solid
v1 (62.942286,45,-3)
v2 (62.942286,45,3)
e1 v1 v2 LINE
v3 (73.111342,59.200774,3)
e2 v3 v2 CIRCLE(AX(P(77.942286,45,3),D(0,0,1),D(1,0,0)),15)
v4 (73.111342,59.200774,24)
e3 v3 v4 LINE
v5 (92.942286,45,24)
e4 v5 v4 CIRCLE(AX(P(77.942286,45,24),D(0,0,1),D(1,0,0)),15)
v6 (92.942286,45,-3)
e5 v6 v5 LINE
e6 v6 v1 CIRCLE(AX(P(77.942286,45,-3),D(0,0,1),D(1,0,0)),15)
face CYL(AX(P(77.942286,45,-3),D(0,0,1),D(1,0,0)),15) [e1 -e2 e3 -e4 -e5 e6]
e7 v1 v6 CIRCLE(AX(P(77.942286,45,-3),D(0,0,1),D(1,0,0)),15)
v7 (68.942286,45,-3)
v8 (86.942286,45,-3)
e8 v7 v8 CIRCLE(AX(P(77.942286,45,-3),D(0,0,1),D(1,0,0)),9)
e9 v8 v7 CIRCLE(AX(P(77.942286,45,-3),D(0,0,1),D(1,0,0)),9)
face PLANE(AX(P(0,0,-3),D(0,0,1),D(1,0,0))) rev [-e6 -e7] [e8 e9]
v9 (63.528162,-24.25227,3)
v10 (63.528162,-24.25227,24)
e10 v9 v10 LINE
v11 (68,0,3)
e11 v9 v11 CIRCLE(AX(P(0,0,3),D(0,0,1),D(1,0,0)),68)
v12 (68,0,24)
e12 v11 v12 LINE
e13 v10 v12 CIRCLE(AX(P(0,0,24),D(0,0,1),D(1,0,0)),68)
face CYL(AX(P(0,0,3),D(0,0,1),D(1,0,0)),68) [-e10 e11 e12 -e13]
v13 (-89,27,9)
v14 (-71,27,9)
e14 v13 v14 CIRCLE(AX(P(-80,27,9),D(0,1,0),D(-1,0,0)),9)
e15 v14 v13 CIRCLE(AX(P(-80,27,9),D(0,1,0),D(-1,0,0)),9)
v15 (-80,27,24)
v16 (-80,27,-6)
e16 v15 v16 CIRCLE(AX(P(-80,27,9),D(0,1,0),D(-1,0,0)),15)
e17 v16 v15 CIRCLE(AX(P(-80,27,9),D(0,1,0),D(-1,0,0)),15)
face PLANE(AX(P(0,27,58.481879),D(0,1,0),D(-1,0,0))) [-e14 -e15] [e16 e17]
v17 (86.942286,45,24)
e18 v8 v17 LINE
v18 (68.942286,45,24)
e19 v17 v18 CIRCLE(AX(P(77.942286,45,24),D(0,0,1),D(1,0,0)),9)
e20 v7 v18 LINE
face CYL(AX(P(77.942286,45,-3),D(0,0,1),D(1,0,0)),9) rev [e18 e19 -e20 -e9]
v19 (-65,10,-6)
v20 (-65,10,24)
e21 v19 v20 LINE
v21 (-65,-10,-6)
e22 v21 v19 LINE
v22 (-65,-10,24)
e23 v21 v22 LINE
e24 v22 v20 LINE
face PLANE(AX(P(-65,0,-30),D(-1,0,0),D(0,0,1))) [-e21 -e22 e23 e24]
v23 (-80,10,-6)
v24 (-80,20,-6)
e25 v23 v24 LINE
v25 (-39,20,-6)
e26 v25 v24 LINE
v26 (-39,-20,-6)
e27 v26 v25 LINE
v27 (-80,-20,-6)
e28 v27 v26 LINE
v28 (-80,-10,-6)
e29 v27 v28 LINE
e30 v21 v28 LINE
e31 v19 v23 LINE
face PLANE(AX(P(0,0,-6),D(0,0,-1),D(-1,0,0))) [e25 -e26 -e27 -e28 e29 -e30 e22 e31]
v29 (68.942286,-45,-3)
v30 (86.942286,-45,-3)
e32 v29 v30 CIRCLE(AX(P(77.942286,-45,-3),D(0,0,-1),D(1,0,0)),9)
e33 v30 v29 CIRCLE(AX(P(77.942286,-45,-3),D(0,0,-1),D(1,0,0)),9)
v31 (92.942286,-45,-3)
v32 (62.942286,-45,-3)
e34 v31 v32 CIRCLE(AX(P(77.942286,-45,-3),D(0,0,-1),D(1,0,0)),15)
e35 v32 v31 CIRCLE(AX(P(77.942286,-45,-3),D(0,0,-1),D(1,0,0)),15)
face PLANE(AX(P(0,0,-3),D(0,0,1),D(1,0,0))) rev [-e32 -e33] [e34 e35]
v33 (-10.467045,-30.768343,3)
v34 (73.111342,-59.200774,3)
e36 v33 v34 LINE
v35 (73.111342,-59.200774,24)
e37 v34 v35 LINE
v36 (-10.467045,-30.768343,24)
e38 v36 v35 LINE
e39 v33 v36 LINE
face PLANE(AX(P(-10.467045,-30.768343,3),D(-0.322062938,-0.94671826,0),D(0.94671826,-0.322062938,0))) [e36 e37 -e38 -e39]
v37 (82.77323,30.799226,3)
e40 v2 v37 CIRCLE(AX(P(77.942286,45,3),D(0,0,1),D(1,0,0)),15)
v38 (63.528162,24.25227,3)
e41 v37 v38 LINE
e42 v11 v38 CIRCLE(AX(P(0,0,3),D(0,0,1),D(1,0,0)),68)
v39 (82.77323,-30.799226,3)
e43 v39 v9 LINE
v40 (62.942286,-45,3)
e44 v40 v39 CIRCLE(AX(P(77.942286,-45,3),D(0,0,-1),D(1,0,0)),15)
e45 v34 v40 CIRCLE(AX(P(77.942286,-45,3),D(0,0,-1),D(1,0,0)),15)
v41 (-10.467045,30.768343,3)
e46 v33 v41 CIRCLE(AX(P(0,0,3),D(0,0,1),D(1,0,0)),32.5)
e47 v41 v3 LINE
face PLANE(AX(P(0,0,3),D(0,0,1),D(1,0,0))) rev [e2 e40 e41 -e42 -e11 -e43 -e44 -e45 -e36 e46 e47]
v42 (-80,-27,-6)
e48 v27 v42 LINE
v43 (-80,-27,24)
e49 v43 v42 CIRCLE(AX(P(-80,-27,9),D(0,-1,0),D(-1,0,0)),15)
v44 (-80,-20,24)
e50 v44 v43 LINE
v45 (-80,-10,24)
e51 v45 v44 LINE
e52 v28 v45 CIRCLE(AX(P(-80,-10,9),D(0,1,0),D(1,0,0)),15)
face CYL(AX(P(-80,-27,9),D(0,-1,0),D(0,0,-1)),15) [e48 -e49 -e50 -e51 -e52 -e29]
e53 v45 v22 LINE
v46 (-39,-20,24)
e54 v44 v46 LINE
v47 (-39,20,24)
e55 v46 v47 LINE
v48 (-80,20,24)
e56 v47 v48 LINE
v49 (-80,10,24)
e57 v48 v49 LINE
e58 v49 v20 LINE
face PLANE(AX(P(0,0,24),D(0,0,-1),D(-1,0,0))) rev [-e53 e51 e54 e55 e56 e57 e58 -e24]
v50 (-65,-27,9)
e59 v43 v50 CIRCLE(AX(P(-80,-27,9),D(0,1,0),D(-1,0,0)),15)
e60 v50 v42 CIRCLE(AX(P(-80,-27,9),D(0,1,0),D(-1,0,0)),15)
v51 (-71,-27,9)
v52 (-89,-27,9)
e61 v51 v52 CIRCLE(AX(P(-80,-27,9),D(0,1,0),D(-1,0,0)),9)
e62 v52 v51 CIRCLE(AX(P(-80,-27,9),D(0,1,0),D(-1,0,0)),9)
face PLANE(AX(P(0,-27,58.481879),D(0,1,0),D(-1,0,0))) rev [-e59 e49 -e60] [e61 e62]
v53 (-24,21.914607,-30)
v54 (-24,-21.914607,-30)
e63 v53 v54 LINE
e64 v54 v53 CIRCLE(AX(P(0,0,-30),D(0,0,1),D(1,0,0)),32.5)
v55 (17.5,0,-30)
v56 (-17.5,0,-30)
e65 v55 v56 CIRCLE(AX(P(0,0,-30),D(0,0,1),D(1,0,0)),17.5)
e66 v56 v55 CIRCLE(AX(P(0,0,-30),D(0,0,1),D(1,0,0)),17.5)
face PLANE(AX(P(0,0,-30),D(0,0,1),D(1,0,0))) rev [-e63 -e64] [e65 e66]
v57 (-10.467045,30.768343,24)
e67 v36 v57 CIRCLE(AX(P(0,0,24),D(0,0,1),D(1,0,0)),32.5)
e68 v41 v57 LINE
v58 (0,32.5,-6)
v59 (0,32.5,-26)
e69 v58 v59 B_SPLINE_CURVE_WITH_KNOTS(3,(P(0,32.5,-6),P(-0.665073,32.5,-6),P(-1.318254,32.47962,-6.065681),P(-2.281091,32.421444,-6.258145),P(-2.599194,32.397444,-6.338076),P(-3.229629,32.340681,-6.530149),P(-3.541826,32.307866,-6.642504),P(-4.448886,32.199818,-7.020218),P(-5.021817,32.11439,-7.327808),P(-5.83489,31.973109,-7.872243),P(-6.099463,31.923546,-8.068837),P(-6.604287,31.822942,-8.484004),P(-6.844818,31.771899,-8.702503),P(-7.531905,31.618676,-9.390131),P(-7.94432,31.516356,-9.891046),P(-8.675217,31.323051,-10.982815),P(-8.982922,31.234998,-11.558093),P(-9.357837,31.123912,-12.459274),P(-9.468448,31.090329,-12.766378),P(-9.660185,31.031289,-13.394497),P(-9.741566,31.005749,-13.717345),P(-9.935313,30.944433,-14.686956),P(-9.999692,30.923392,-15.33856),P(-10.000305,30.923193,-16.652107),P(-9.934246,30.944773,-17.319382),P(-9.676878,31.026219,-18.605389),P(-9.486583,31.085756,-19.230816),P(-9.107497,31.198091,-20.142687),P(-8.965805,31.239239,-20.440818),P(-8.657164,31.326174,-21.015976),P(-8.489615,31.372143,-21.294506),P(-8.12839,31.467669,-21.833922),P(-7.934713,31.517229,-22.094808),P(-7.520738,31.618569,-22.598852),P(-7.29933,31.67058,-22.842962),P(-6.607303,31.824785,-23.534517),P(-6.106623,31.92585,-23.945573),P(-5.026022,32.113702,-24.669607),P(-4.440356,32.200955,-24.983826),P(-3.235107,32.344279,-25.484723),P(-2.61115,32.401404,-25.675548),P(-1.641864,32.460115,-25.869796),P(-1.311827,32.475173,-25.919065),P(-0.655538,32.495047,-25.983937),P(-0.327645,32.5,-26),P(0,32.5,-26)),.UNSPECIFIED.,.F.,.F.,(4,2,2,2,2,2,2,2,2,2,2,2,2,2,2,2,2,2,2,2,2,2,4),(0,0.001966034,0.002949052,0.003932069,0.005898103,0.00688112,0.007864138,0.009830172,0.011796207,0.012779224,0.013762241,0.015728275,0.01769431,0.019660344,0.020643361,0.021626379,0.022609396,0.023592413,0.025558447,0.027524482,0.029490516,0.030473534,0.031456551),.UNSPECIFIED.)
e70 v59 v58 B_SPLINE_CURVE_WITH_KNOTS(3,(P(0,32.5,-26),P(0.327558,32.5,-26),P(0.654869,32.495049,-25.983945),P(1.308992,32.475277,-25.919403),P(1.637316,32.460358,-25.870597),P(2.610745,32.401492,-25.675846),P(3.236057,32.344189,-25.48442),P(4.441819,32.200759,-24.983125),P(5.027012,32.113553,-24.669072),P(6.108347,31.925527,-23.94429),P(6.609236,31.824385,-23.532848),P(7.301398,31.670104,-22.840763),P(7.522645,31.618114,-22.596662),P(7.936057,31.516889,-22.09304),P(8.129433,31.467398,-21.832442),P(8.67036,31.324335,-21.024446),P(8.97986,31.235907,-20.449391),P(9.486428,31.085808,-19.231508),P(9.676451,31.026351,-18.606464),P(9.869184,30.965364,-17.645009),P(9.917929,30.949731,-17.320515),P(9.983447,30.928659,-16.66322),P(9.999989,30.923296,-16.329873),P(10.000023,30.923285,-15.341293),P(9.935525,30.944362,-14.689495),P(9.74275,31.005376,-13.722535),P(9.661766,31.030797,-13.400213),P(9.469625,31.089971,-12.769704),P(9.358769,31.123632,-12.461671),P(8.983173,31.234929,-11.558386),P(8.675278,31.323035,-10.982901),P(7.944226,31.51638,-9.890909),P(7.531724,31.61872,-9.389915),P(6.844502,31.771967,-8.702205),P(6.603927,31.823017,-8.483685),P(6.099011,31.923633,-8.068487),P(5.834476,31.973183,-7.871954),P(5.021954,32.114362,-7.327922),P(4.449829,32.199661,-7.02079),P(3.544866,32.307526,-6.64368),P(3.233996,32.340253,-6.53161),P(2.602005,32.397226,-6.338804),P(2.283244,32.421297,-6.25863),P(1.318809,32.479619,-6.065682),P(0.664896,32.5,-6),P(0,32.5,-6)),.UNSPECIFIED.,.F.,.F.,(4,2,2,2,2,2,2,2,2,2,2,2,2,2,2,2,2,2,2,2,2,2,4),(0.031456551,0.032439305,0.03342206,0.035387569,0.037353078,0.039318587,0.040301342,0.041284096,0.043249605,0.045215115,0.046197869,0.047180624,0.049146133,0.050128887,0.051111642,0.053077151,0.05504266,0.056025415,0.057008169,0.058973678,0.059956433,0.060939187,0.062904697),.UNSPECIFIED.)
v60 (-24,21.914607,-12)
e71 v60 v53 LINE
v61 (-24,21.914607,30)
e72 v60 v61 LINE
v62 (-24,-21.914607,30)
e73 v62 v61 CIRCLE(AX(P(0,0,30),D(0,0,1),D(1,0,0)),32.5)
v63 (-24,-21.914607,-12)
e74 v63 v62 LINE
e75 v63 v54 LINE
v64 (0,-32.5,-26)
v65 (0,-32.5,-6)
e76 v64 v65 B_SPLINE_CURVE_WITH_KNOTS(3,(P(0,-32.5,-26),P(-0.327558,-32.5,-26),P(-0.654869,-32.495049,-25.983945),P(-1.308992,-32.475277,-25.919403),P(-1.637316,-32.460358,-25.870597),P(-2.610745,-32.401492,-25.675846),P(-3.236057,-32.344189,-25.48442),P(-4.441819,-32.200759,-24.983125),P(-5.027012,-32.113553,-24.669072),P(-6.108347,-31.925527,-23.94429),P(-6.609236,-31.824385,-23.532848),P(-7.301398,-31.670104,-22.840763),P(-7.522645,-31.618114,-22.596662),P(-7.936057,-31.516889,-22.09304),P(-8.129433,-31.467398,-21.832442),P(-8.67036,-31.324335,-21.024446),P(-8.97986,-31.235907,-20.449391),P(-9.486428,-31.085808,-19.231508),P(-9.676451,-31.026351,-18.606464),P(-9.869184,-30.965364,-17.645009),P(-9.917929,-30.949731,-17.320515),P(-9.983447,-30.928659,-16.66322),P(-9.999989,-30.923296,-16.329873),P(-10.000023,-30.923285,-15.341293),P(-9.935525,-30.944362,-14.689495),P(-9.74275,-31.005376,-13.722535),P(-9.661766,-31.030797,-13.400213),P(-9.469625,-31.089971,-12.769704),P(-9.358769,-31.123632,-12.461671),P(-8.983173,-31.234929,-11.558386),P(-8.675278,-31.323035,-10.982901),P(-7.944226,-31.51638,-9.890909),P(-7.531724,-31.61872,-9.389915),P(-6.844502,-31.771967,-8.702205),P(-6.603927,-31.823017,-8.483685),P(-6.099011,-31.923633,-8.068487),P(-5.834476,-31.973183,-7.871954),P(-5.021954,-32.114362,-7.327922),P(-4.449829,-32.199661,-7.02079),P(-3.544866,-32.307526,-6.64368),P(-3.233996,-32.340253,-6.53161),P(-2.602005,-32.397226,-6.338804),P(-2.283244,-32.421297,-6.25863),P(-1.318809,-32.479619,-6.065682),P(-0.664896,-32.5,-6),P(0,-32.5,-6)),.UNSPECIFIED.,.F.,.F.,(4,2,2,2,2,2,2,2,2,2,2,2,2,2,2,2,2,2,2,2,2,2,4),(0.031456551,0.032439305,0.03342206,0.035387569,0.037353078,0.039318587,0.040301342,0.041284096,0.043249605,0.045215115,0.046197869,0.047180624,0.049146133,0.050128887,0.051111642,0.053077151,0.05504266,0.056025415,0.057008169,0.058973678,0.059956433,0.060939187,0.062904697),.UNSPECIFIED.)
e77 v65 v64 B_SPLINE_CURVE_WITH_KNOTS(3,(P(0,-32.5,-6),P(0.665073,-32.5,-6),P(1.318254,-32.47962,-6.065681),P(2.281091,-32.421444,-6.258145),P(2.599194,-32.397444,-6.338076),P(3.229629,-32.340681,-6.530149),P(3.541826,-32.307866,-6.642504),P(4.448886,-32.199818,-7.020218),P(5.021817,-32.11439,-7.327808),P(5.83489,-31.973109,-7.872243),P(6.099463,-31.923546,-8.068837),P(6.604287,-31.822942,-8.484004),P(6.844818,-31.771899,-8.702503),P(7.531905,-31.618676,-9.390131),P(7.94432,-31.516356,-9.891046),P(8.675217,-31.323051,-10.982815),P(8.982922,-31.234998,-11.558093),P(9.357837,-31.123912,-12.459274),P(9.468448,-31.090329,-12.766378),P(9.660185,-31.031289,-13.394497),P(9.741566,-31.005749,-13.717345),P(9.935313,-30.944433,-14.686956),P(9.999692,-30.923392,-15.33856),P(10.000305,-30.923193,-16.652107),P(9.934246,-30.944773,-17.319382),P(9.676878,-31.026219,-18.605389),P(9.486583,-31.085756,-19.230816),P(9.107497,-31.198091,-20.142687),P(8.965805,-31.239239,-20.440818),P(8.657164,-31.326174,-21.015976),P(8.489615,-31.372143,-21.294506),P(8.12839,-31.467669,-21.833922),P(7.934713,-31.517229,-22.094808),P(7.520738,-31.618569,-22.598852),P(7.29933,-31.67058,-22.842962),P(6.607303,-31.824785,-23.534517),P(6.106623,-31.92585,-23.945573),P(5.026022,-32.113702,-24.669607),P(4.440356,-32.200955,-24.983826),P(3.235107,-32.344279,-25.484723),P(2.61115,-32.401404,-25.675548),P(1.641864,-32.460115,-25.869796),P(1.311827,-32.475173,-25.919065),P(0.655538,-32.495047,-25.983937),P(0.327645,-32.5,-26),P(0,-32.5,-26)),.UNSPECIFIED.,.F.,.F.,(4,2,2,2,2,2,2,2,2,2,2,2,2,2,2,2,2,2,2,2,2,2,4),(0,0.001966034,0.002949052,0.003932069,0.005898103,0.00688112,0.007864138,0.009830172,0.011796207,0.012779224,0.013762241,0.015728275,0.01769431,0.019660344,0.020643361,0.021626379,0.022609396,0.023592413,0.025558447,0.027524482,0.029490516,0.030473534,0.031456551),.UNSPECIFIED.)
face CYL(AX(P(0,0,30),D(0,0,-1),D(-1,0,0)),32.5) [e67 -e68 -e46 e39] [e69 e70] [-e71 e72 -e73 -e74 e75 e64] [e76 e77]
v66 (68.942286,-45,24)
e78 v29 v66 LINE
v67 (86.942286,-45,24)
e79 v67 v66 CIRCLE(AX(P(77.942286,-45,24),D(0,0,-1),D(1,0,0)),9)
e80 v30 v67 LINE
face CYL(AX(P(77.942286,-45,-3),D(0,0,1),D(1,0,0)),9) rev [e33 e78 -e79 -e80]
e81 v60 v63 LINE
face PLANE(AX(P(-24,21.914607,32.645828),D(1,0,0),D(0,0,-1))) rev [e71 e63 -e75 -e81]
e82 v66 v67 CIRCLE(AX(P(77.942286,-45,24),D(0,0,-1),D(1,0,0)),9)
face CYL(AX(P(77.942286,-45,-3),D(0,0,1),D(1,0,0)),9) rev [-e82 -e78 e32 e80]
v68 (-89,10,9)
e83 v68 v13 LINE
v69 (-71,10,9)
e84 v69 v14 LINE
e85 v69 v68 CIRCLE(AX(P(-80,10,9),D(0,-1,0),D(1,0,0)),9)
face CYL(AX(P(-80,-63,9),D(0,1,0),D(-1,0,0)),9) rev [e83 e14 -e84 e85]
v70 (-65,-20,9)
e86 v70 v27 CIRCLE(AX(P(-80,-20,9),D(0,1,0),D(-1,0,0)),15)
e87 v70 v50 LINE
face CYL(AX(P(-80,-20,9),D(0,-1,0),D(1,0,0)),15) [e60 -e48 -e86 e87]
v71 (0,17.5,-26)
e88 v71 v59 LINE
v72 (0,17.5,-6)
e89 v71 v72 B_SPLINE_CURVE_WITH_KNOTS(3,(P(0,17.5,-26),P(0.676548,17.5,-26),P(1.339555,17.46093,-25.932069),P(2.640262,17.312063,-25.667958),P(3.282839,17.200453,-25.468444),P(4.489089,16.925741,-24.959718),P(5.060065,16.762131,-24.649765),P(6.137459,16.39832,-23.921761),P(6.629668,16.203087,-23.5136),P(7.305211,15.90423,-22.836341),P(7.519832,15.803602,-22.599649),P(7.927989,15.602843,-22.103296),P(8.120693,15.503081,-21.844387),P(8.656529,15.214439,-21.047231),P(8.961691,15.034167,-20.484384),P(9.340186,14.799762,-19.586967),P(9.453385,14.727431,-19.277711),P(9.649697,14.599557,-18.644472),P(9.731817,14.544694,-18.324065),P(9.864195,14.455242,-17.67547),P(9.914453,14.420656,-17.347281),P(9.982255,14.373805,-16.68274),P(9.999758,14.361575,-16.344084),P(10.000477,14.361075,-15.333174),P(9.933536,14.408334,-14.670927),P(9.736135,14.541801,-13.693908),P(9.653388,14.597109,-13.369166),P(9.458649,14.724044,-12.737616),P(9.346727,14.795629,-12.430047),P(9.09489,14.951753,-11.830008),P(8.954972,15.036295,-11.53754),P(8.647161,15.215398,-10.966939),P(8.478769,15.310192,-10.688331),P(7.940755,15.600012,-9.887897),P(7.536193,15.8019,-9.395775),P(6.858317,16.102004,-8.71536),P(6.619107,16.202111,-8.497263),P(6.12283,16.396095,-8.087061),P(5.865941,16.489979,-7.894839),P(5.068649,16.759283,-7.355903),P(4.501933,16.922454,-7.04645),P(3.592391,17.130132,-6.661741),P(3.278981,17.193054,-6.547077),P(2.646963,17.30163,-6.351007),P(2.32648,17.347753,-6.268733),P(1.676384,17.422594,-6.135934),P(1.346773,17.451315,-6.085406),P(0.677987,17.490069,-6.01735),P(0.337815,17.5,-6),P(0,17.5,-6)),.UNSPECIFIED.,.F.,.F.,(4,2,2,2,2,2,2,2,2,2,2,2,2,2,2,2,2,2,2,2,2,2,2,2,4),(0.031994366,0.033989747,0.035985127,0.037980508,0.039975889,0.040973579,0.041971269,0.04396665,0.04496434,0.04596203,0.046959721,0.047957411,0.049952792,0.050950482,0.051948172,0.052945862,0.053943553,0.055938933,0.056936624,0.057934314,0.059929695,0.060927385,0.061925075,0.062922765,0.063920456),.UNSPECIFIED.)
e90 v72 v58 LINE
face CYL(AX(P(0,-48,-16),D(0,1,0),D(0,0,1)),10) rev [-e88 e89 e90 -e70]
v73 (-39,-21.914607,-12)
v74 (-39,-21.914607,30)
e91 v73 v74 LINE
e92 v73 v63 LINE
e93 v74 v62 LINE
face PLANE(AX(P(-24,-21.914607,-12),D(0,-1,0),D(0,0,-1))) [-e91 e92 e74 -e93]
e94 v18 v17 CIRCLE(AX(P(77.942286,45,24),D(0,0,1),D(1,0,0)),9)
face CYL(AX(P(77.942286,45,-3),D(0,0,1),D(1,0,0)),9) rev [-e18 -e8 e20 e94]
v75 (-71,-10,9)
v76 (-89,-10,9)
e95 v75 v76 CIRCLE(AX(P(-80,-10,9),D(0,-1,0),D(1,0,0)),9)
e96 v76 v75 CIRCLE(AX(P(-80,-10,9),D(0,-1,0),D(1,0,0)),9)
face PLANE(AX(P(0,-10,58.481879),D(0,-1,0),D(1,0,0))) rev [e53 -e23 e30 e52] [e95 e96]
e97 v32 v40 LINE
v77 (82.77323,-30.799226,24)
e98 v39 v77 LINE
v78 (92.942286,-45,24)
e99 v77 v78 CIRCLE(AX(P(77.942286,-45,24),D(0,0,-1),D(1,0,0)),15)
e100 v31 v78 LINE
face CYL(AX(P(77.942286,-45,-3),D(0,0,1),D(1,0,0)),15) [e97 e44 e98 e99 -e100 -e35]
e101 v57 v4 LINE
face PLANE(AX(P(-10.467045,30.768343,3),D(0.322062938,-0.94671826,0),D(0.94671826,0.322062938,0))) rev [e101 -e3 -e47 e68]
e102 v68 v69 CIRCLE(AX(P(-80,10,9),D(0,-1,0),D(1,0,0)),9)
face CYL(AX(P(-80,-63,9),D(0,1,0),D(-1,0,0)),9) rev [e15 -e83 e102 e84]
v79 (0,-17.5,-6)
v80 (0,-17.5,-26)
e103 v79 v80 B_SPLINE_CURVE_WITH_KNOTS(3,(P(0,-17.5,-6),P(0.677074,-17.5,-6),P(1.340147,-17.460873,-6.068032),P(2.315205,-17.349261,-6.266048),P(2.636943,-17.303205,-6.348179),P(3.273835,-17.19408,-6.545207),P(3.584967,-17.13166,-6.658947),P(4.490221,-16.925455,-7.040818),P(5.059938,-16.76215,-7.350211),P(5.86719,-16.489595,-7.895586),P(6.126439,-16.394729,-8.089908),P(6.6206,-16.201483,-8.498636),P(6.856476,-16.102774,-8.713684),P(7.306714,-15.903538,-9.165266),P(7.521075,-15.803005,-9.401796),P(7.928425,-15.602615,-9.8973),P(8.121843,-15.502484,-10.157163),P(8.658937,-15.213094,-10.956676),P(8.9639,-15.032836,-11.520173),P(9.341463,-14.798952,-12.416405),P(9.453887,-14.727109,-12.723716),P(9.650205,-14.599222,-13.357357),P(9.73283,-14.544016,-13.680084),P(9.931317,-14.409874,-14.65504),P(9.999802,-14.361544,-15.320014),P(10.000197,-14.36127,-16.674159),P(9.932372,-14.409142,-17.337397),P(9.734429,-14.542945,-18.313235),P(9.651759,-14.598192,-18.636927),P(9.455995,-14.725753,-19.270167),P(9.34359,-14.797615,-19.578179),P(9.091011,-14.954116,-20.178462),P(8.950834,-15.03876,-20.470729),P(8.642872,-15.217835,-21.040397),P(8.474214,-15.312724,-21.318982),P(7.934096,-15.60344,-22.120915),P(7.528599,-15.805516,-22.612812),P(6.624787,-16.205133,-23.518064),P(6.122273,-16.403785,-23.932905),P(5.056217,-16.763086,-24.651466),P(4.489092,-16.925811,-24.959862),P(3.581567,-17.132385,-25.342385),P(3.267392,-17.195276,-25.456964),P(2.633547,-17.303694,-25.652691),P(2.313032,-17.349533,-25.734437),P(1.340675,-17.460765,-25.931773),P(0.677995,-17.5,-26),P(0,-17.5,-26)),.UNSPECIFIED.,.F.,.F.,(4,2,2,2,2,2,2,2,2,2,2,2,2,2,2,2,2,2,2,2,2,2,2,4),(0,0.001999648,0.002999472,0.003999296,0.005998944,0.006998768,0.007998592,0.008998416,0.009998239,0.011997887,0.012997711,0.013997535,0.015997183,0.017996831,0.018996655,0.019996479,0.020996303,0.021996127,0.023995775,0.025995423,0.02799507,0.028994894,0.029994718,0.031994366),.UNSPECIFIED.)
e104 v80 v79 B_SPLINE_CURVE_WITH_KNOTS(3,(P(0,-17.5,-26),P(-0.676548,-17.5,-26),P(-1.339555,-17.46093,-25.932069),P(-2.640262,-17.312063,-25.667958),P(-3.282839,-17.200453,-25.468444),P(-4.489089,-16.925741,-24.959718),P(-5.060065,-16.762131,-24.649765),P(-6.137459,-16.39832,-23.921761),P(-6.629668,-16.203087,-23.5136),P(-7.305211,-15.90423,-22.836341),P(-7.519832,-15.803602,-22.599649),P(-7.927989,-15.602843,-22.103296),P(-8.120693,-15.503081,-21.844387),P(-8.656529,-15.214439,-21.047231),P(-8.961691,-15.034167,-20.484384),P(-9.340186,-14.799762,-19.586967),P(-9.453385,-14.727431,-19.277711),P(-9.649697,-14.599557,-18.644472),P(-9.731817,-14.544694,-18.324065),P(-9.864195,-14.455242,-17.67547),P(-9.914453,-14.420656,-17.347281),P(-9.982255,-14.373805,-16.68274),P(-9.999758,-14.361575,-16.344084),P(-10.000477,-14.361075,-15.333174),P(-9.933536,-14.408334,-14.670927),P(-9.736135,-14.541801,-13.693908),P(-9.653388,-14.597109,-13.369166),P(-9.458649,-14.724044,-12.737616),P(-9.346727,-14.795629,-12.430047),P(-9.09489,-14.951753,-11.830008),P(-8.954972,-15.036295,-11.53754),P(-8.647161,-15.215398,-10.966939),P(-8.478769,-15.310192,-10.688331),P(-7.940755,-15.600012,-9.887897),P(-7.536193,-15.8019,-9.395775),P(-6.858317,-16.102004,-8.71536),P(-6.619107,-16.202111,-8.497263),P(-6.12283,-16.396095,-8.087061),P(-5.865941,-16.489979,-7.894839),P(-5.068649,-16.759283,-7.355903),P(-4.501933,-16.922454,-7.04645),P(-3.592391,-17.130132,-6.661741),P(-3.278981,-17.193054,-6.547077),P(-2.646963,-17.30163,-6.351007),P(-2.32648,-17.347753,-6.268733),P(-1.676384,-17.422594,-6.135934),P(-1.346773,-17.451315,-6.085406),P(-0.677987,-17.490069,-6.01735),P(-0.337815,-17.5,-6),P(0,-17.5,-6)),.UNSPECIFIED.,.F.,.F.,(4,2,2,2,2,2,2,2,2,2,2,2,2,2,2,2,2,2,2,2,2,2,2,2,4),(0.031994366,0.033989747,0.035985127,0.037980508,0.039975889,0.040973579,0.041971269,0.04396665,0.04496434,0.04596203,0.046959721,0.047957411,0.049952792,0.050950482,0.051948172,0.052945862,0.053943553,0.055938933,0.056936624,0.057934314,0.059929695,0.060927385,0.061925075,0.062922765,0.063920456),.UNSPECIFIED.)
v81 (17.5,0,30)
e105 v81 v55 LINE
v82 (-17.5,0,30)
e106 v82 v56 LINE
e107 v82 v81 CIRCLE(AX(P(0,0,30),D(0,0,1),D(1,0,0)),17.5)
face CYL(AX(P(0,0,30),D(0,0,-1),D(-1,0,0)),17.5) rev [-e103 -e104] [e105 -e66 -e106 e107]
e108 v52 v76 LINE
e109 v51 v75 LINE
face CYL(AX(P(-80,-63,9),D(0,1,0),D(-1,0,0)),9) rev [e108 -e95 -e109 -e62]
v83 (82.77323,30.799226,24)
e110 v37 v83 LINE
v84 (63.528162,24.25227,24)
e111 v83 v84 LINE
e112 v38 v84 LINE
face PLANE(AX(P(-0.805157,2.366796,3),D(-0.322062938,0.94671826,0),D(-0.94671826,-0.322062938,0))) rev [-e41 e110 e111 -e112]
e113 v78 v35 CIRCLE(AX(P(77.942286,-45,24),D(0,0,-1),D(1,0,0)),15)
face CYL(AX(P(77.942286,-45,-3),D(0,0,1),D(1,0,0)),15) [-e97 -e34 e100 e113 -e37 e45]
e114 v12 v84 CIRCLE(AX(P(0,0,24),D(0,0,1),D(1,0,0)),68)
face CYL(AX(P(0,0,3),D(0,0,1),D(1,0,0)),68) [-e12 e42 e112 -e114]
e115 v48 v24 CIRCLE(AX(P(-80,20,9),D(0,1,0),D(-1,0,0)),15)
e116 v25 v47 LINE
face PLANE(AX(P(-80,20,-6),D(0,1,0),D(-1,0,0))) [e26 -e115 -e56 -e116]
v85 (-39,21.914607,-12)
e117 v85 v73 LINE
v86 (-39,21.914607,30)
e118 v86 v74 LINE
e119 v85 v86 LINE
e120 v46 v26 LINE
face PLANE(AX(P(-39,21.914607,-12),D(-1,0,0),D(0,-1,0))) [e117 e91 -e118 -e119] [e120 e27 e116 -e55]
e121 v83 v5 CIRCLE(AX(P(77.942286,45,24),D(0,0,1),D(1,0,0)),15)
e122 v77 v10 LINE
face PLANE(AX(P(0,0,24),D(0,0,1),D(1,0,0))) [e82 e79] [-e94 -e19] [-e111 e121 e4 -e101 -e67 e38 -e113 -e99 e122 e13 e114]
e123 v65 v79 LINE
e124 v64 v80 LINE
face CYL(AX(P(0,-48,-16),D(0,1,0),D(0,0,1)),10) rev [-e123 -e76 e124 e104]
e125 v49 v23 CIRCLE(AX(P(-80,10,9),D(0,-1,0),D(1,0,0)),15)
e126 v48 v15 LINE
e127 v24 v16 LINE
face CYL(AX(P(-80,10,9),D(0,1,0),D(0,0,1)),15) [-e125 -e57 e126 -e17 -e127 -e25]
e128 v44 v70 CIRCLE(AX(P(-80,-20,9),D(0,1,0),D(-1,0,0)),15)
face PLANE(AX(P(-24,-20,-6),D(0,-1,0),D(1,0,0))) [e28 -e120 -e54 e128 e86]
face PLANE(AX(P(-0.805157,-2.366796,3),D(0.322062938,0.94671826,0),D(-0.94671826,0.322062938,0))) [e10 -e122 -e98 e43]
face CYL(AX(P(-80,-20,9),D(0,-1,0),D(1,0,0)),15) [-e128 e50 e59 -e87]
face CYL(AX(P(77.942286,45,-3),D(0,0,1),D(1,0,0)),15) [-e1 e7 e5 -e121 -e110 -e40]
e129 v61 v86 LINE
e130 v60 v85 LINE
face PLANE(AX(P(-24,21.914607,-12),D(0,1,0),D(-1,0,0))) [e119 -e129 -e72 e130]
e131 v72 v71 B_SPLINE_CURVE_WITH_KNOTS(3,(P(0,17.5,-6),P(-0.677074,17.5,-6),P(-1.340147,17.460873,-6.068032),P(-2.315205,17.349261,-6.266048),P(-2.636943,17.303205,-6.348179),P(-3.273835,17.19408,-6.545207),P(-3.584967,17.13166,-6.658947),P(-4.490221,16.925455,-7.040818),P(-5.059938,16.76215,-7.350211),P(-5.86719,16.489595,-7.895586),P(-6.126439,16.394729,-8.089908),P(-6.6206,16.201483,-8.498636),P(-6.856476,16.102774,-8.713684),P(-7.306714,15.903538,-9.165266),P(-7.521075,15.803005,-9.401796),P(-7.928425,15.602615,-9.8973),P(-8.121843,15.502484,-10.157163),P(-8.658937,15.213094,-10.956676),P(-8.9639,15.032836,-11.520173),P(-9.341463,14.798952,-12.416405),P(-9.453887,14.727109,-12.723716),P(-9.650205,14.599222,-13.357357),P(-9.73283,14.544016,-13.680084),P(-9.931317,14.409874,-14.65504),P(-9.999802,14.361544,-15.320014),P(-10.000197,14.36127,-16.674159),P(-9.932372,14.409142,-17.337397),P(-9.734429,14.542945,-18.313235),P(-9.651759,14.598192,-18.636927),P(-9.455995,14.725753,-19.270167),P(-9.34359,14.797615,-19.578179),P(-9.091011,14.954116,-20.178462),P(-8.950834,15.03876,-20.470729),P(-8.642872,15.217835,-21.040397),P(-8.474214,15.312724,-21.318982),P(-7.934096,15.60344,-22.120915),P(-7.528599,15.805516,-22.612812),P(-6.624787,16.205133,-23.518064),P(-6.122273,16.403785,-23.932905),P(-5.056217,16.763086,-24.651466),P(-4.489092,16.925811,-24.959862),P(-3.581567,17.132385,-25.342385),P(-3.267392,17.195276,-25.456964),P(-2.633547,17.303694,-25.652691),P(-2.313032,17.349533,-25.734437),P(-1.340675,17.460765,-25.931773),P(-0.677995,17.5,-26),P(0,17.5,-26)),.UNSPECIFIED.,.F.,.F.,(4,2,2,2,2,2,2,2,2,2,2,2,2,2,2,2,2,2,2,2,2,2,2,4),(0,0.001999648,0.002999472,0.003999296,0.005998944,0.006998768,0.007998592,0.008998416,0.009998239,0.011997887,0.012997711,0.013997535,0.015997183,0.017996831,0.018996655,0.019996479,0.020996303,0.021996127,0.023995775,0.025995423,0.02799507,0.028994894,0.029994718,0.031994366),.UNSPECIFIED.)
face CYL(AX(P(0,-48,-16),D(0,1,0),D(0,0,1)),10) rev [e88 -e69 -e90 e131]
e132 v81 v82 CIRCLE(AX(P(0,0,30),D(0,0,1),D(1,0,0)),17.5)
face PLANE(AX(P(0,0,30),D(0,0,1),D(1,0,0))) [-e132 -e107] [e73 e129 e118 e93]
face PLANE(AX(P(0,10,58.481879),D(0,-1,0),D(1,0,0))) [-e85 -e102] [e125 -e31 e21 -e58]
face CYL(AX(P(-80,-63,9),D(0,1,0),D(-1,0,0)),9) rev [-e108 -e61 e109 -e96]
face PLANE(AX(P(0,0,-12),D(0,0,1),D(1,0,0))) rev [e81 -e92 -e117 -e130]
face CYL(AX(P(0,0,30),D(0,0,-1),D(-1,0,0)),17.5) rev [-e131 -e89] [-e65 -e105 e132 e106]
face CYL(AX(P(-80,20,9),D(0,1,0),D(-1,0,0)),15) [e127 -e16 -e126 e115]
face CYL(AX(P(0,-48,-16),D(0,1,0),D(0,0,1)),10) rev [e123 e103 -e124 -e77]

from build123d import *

# Parameters (mm, degrees)
HUB_SKETCH_R                 = 32.5
HUB_SKETCH_R_2               = 17.5
HUB_BOSS_65_DEPTH            = 30
ARM_WEB_DEPTH                = 21
SKETCH3_3_R                  = 15
SKETCH3_3_R_2                = 9
ARM_END_LUGS_DEPTH           = 27
CROSS_HOLE_SKETCH_R          = 10
CROSS_HOLE_14_DEPTH          = 48
CLEVIS_BLOCK_SKETCH_W        = 56
CLEVIS_BLOCK_SKETCH_H        = 40
CLEVIS_BLOCK_DEPTH           = 30
REAR_BOSS_SKETCH_W           = 15
REAR_BOSS_SKETCH_H           = 43.829214002
REAR_BOSS_DEPTH              = 42
CLEVIS_ARM_SKETCH_W          = 15
CLEVIS_ARM_SKETCH_H          = 10
CLEVIS_ARM_DEPTH             = 30
CLEVIS_SLOT_DEPTH            = 118.987287481
CLEVIS_SLOT_DEPTH_BACK       = 42
SKETCH8_3_W                  = 15
SKETCH8_3_H                  = 20
CLEVIS_PIN_HOLE_SKETCH_R     = 9
CLEVIS_PIN_HOLE_18_DEPTH     = 90
CLEVIS_RECESS_DEPTH          = 7
CLEVIS_BLOCK_FILLET_A_RADIUS = 15
CLEVIS_BLOCK_FILLET_A_LENGTH = 17
CLEVIS_BLOCK_FILLET_B_RADIUS = 15
CLEVIS_BLOCK_FILLET_B_LENGTH = 17
REAR_START                   = -18
REAR_BOSS_CUT_DEPTH          = 18


with BuildPart() as part:
    # Hub Sketch → Hub Boss _65 (new, symmetric)
    with BuildSketch(Plane.XY):
        Circle(HUB_SKETCH_R)
        Circle(HUB_SKETCH_R_2, mode=Mode.SUBTRACT)
    extrude(amount=HUB_BOSS_65_DEPTH, both=True)

    # Arm Profile Sketch → Arm Web (add)
    with BuildSketch(Plane.XY.offset(24)):
        with BuildLine():
            Line((63.528162364, 24.252269722), (82.77322949, 30.799225786))
            ThreePointArc((82.77322949, 30.799225786), (63.741512282, 40.169056393), (73.111342275, 59.200773903))
            Line((73.111342275, 59.200773903), (-10.467045475, 30.768343456))
            ThreePointArc((-10.467045475, 30.768343456), (18.921826313, 26.423748579), (32.5, 0))
            ThreePointArc((32.5, 0), (18.921826313, -26.423748579), (-10.467045475, -30.768343456))
            Line((-10.467045475, -30.768343456), (73.111342275, -59.200773903))
            ThreePointArc((73.111342275, -59.200773903), (63.741512551, -40.169055602), (82.773231072, -30.799226324))
            Line((82.773231072, -30.799226324), (63.528162364, -24.252269722))
            ThreePointArc((63.528162364, -24.252269722), (68, 0), (63.528162364, 24.252269722))
        make_face()
    extrude(amount=-ARM_WEB_DEPTH)

    # Sketch3_3 → Arm End Lugs (add)
    # profile 1 of 2: a face of its own
    with BuildSketch(Plane.XY.offset(24)):
        with Locations((77.942286341, 45)):
            Circle(SKETCH3_3_R)
        with Locations((77.942286341, 45)):
            Circle(SKETCH3_3_R_2, mode=Mode.SUBTRACT)
    # profile 2 of 2: a face of its own
    with BuildSketch(Plane.XY.offset(24)):
        with Locations((77.942286341, -45)):
            Circle(SKETCH3_3_R)
        with Locations((77.942286341, -45)):
            Circle(SKETCH3_3_R_2, mode=Mode.SUBTRACT)
    extrude(amount=-ARM_END_LUGS_DEPTH)

    # Cross Hole Sketch → Cross Hole _14 (cut, symmetric)
    with BuildSketch(Plane(origin=(0, 0, 0), x_dir=(1, 0, 0), z_dir=(0, 1, 0))):
        with Locations(Location((0, 16, 0), (0, 0, 270))):
            Circle(CROSS_HOLE_SKETCH_R)
    extrude(amount=CROSS_HOLE_14_DEPTH, both=True, mode=Mode.SUBTRACT)

    # Clevis Block Sketch → Clevis Block (add)
    with BuildSketch(Plane.XY.offset(24)):
        with Locations((-52, 0)):
            Rectangle(CLEVIS_BLOCK_SKETCH_W, CLEVIS_BLOCK_SKETCH_H)
    extrude(amount=-CLEVIS_BLOCK_DEPTH)

    # Rear Boss Sketch → Rear Boss (add)
    with BuildSketch(Plane.XY.offset(30)):
        with Locations((-31.5, 0)):
            Rectangle(REAR_BOSS_SKETCH_W, REAR_BOSS_SKETCH_H)
    extrude(amount=-REAR_BOSS_DEPTH)

    # Clevis Arm Sketch → Clevis Arm (add)
    with BuildSketch(Plane(origin=(0, 0, -6), x_dir=(-1, 0, 0), z_dir=(0, 0, -1))):
        Polygon((80, 20), (80, 10), (95, 10), (95, 27), (65, 27), (65, 20), align=None)
        with Locations((72.5, 15)):
            Rectangle(CLEVIS_ARM_SKETCH_W, CLEVIS_ARM_SKETCH_H)
        Polygon((65, -27), (95, -27), (95, -10), (80, -10), (80, -20), (65, -20), align=None)
        with Locations((72.5, -15)):
            Rectangle(CLEVIS_ARM_SKETCH_W, CLEVIS_ARM_SKETCH_H)
    extrude(amount=-CLEVIS_ARM_DEPTH)

    # Sketch8_3 → Clevis Slot (cut, two sides: drawn at the far end of the back side and taken through both)
    with BuildSketch(Plane(origin=(0, 0, -6), x_dir=(-1, 0, 0), z_dir=(0, 0, -1)).offset(-CLEVIS_SLOT_DEPTH_BACK)):
        with Locations((72.5, 0)):
            Rectangle(SKETCH8_3_W, SKETCH8_3_H)
    extrude(amount=CLEVIS_SLOT_DEPTH + CLEVIS_SLOT_DEPTH_BACK, mode=Mode.SUBTRACT)

    # Clevis Pin Hole Sketch → Clevis Pin Hole _18 (cut)
    with BuildSketch(Plane(origin=(0, 27, 0), x_dir=(1, 0, 0), z_dir=(0, 1, 0))):
        with Locations(Location((-80, -9, 0), (0, 0, 180))):
            Circle(CLEVIS_PIN_HOLE_SKETCH_R)
    extrude(amount=-CLEVIS_PIN_HOLE_18_DEPTH, mode=Mode.SUBTRACT)

    # Clevis Recess Sketch → Clevis Recess (cut)
    with BuildSketch(Plane(origin=(0, 27, 0), x_dir=(1, 0, 0), z_dir=(0, 1, 0))):
        with BuildLine():
            ThreePointArc((-80, 6), (-69.393398282, 1.606601718), (-65, -9))
            Line((-65, -9), (-65, 6))
            Line((-65, 6), (-80, 6))
        make_face()
        with BuildLine():
            Line((-80, -24), (-65, -24))
            Line((-65, -24), (-65, -9))
            ThreePointArc((-65, -9), (-69.393398282, -19.606601718), (-80, -24))
        make_face()
    clevis_recess = extrude(amount=-CLEVIS_RECESS_DEPTH, mode=Mode.SUBTRACT)

    # Clevis Recess Mirror: Clevis Recess across plane
    add(clevis_recess.mirror(Plane.ZX), mode=Mode.SUBTRACT)

    # Clevis Block Fillet A: full round fillet: the end face becomes a half cylinder, R = half its width
    clevis_block_fillet_a_face = Plane((-95, 18.5, 9), x_dir=(0, -1, 0), z_dir=(-1, 0, 0))  # on the end face: x along it, z out of the body
    clevis_block_fillet_a_slab = clevis_block_fillet_a_face.offset(-CLEVIS_BLOCK_FILLET_A_RADIUS / 2) * Box(CLEVIS_BLOCK_FILLET_A_LENGTH, 2 * CLEVIS_BLOCK_FILLET_A_RADIUS, CLEVIS_BLOCK_FILLET_A_RADIUS, mode=Mode.PRIVATE)  # the body's end, R deep
    clevis_block_fillet_a_round = Plane((-80, 18.5, 9), x_dir=(-1, 0, 0), z_dir=(0, -1, 0)) * Cylinder(CLEVIS_BLOCK_FILLET_A_RADIUS, CLEVIS_BLOCK_FILLET_A_LENGTH, mode=Mode.PRIVATE)  # its axis R under the face
    add(clevis_block_fillet_a_slab - clevis_block_fillet_a_round, mode=Mode.SUBTRACT)

    # Clevis Block Fillet B: full round fillet: the end face becomes a half cylinder, R = half its width
    clevis_block_fillet_b_face = Plane((-95, -18.5, 9), x_dir=(0, 1, 0), z_dir=(-1, 0, 0))  # on the end face: x along it, z out of the body
    clevis_block_fillet_b_slab = clevis_block_fillet_b_face.offset(-CLEVIS_BLOCK_FILLET_B_RADIUS / 2) * Box(CLEVIS_BLOCK_FILLET_B_LENGTH, 2 * CLEVIS_BLOCK_FILLET_B_RADIUS, CLEVIS_BLOCK_FILLET_B_RADIUS, mode=Mode.PRIVATE)  # the body's end, R deep
    clevis_block_fillet_b_round = Plane((-80, -18.5, 9), x_dir=(-1, 0, 0), z_dir=(0, 1, 0)) * Cylinder(CLEVIS_BLOCK_FILLET_B_RADIUS, CLEVIS_BLOCK_FILLET_B_LENGTH, mode=Mode.PRIVATE)  # its axis R under the face
    add(clevis_block_fillet_b_slab - clevis_block_fillet_b_round, mode=Mode.SUBTRACT)

    # Rear Boss Cut Sketch → Rear Boss Cut (cut)
    with BuildSketch(Plane(origin=(0, 0, -30), x_dir=(-1, 0, 0), z_dir=(0, 0, -1)).offset(REAR_START)):
        with BuildLine():
            Line((24, 21.914607001), (24, -21.914607001))
            ThreePointArc((24, -21.914607001), (32.5, 0), (24, 21.914607001))
        make_face()
    extrude(amount=REAR_BOSS_CUT_DEPTH, mode=Mode.SUBTRACT)


solid = part.part
